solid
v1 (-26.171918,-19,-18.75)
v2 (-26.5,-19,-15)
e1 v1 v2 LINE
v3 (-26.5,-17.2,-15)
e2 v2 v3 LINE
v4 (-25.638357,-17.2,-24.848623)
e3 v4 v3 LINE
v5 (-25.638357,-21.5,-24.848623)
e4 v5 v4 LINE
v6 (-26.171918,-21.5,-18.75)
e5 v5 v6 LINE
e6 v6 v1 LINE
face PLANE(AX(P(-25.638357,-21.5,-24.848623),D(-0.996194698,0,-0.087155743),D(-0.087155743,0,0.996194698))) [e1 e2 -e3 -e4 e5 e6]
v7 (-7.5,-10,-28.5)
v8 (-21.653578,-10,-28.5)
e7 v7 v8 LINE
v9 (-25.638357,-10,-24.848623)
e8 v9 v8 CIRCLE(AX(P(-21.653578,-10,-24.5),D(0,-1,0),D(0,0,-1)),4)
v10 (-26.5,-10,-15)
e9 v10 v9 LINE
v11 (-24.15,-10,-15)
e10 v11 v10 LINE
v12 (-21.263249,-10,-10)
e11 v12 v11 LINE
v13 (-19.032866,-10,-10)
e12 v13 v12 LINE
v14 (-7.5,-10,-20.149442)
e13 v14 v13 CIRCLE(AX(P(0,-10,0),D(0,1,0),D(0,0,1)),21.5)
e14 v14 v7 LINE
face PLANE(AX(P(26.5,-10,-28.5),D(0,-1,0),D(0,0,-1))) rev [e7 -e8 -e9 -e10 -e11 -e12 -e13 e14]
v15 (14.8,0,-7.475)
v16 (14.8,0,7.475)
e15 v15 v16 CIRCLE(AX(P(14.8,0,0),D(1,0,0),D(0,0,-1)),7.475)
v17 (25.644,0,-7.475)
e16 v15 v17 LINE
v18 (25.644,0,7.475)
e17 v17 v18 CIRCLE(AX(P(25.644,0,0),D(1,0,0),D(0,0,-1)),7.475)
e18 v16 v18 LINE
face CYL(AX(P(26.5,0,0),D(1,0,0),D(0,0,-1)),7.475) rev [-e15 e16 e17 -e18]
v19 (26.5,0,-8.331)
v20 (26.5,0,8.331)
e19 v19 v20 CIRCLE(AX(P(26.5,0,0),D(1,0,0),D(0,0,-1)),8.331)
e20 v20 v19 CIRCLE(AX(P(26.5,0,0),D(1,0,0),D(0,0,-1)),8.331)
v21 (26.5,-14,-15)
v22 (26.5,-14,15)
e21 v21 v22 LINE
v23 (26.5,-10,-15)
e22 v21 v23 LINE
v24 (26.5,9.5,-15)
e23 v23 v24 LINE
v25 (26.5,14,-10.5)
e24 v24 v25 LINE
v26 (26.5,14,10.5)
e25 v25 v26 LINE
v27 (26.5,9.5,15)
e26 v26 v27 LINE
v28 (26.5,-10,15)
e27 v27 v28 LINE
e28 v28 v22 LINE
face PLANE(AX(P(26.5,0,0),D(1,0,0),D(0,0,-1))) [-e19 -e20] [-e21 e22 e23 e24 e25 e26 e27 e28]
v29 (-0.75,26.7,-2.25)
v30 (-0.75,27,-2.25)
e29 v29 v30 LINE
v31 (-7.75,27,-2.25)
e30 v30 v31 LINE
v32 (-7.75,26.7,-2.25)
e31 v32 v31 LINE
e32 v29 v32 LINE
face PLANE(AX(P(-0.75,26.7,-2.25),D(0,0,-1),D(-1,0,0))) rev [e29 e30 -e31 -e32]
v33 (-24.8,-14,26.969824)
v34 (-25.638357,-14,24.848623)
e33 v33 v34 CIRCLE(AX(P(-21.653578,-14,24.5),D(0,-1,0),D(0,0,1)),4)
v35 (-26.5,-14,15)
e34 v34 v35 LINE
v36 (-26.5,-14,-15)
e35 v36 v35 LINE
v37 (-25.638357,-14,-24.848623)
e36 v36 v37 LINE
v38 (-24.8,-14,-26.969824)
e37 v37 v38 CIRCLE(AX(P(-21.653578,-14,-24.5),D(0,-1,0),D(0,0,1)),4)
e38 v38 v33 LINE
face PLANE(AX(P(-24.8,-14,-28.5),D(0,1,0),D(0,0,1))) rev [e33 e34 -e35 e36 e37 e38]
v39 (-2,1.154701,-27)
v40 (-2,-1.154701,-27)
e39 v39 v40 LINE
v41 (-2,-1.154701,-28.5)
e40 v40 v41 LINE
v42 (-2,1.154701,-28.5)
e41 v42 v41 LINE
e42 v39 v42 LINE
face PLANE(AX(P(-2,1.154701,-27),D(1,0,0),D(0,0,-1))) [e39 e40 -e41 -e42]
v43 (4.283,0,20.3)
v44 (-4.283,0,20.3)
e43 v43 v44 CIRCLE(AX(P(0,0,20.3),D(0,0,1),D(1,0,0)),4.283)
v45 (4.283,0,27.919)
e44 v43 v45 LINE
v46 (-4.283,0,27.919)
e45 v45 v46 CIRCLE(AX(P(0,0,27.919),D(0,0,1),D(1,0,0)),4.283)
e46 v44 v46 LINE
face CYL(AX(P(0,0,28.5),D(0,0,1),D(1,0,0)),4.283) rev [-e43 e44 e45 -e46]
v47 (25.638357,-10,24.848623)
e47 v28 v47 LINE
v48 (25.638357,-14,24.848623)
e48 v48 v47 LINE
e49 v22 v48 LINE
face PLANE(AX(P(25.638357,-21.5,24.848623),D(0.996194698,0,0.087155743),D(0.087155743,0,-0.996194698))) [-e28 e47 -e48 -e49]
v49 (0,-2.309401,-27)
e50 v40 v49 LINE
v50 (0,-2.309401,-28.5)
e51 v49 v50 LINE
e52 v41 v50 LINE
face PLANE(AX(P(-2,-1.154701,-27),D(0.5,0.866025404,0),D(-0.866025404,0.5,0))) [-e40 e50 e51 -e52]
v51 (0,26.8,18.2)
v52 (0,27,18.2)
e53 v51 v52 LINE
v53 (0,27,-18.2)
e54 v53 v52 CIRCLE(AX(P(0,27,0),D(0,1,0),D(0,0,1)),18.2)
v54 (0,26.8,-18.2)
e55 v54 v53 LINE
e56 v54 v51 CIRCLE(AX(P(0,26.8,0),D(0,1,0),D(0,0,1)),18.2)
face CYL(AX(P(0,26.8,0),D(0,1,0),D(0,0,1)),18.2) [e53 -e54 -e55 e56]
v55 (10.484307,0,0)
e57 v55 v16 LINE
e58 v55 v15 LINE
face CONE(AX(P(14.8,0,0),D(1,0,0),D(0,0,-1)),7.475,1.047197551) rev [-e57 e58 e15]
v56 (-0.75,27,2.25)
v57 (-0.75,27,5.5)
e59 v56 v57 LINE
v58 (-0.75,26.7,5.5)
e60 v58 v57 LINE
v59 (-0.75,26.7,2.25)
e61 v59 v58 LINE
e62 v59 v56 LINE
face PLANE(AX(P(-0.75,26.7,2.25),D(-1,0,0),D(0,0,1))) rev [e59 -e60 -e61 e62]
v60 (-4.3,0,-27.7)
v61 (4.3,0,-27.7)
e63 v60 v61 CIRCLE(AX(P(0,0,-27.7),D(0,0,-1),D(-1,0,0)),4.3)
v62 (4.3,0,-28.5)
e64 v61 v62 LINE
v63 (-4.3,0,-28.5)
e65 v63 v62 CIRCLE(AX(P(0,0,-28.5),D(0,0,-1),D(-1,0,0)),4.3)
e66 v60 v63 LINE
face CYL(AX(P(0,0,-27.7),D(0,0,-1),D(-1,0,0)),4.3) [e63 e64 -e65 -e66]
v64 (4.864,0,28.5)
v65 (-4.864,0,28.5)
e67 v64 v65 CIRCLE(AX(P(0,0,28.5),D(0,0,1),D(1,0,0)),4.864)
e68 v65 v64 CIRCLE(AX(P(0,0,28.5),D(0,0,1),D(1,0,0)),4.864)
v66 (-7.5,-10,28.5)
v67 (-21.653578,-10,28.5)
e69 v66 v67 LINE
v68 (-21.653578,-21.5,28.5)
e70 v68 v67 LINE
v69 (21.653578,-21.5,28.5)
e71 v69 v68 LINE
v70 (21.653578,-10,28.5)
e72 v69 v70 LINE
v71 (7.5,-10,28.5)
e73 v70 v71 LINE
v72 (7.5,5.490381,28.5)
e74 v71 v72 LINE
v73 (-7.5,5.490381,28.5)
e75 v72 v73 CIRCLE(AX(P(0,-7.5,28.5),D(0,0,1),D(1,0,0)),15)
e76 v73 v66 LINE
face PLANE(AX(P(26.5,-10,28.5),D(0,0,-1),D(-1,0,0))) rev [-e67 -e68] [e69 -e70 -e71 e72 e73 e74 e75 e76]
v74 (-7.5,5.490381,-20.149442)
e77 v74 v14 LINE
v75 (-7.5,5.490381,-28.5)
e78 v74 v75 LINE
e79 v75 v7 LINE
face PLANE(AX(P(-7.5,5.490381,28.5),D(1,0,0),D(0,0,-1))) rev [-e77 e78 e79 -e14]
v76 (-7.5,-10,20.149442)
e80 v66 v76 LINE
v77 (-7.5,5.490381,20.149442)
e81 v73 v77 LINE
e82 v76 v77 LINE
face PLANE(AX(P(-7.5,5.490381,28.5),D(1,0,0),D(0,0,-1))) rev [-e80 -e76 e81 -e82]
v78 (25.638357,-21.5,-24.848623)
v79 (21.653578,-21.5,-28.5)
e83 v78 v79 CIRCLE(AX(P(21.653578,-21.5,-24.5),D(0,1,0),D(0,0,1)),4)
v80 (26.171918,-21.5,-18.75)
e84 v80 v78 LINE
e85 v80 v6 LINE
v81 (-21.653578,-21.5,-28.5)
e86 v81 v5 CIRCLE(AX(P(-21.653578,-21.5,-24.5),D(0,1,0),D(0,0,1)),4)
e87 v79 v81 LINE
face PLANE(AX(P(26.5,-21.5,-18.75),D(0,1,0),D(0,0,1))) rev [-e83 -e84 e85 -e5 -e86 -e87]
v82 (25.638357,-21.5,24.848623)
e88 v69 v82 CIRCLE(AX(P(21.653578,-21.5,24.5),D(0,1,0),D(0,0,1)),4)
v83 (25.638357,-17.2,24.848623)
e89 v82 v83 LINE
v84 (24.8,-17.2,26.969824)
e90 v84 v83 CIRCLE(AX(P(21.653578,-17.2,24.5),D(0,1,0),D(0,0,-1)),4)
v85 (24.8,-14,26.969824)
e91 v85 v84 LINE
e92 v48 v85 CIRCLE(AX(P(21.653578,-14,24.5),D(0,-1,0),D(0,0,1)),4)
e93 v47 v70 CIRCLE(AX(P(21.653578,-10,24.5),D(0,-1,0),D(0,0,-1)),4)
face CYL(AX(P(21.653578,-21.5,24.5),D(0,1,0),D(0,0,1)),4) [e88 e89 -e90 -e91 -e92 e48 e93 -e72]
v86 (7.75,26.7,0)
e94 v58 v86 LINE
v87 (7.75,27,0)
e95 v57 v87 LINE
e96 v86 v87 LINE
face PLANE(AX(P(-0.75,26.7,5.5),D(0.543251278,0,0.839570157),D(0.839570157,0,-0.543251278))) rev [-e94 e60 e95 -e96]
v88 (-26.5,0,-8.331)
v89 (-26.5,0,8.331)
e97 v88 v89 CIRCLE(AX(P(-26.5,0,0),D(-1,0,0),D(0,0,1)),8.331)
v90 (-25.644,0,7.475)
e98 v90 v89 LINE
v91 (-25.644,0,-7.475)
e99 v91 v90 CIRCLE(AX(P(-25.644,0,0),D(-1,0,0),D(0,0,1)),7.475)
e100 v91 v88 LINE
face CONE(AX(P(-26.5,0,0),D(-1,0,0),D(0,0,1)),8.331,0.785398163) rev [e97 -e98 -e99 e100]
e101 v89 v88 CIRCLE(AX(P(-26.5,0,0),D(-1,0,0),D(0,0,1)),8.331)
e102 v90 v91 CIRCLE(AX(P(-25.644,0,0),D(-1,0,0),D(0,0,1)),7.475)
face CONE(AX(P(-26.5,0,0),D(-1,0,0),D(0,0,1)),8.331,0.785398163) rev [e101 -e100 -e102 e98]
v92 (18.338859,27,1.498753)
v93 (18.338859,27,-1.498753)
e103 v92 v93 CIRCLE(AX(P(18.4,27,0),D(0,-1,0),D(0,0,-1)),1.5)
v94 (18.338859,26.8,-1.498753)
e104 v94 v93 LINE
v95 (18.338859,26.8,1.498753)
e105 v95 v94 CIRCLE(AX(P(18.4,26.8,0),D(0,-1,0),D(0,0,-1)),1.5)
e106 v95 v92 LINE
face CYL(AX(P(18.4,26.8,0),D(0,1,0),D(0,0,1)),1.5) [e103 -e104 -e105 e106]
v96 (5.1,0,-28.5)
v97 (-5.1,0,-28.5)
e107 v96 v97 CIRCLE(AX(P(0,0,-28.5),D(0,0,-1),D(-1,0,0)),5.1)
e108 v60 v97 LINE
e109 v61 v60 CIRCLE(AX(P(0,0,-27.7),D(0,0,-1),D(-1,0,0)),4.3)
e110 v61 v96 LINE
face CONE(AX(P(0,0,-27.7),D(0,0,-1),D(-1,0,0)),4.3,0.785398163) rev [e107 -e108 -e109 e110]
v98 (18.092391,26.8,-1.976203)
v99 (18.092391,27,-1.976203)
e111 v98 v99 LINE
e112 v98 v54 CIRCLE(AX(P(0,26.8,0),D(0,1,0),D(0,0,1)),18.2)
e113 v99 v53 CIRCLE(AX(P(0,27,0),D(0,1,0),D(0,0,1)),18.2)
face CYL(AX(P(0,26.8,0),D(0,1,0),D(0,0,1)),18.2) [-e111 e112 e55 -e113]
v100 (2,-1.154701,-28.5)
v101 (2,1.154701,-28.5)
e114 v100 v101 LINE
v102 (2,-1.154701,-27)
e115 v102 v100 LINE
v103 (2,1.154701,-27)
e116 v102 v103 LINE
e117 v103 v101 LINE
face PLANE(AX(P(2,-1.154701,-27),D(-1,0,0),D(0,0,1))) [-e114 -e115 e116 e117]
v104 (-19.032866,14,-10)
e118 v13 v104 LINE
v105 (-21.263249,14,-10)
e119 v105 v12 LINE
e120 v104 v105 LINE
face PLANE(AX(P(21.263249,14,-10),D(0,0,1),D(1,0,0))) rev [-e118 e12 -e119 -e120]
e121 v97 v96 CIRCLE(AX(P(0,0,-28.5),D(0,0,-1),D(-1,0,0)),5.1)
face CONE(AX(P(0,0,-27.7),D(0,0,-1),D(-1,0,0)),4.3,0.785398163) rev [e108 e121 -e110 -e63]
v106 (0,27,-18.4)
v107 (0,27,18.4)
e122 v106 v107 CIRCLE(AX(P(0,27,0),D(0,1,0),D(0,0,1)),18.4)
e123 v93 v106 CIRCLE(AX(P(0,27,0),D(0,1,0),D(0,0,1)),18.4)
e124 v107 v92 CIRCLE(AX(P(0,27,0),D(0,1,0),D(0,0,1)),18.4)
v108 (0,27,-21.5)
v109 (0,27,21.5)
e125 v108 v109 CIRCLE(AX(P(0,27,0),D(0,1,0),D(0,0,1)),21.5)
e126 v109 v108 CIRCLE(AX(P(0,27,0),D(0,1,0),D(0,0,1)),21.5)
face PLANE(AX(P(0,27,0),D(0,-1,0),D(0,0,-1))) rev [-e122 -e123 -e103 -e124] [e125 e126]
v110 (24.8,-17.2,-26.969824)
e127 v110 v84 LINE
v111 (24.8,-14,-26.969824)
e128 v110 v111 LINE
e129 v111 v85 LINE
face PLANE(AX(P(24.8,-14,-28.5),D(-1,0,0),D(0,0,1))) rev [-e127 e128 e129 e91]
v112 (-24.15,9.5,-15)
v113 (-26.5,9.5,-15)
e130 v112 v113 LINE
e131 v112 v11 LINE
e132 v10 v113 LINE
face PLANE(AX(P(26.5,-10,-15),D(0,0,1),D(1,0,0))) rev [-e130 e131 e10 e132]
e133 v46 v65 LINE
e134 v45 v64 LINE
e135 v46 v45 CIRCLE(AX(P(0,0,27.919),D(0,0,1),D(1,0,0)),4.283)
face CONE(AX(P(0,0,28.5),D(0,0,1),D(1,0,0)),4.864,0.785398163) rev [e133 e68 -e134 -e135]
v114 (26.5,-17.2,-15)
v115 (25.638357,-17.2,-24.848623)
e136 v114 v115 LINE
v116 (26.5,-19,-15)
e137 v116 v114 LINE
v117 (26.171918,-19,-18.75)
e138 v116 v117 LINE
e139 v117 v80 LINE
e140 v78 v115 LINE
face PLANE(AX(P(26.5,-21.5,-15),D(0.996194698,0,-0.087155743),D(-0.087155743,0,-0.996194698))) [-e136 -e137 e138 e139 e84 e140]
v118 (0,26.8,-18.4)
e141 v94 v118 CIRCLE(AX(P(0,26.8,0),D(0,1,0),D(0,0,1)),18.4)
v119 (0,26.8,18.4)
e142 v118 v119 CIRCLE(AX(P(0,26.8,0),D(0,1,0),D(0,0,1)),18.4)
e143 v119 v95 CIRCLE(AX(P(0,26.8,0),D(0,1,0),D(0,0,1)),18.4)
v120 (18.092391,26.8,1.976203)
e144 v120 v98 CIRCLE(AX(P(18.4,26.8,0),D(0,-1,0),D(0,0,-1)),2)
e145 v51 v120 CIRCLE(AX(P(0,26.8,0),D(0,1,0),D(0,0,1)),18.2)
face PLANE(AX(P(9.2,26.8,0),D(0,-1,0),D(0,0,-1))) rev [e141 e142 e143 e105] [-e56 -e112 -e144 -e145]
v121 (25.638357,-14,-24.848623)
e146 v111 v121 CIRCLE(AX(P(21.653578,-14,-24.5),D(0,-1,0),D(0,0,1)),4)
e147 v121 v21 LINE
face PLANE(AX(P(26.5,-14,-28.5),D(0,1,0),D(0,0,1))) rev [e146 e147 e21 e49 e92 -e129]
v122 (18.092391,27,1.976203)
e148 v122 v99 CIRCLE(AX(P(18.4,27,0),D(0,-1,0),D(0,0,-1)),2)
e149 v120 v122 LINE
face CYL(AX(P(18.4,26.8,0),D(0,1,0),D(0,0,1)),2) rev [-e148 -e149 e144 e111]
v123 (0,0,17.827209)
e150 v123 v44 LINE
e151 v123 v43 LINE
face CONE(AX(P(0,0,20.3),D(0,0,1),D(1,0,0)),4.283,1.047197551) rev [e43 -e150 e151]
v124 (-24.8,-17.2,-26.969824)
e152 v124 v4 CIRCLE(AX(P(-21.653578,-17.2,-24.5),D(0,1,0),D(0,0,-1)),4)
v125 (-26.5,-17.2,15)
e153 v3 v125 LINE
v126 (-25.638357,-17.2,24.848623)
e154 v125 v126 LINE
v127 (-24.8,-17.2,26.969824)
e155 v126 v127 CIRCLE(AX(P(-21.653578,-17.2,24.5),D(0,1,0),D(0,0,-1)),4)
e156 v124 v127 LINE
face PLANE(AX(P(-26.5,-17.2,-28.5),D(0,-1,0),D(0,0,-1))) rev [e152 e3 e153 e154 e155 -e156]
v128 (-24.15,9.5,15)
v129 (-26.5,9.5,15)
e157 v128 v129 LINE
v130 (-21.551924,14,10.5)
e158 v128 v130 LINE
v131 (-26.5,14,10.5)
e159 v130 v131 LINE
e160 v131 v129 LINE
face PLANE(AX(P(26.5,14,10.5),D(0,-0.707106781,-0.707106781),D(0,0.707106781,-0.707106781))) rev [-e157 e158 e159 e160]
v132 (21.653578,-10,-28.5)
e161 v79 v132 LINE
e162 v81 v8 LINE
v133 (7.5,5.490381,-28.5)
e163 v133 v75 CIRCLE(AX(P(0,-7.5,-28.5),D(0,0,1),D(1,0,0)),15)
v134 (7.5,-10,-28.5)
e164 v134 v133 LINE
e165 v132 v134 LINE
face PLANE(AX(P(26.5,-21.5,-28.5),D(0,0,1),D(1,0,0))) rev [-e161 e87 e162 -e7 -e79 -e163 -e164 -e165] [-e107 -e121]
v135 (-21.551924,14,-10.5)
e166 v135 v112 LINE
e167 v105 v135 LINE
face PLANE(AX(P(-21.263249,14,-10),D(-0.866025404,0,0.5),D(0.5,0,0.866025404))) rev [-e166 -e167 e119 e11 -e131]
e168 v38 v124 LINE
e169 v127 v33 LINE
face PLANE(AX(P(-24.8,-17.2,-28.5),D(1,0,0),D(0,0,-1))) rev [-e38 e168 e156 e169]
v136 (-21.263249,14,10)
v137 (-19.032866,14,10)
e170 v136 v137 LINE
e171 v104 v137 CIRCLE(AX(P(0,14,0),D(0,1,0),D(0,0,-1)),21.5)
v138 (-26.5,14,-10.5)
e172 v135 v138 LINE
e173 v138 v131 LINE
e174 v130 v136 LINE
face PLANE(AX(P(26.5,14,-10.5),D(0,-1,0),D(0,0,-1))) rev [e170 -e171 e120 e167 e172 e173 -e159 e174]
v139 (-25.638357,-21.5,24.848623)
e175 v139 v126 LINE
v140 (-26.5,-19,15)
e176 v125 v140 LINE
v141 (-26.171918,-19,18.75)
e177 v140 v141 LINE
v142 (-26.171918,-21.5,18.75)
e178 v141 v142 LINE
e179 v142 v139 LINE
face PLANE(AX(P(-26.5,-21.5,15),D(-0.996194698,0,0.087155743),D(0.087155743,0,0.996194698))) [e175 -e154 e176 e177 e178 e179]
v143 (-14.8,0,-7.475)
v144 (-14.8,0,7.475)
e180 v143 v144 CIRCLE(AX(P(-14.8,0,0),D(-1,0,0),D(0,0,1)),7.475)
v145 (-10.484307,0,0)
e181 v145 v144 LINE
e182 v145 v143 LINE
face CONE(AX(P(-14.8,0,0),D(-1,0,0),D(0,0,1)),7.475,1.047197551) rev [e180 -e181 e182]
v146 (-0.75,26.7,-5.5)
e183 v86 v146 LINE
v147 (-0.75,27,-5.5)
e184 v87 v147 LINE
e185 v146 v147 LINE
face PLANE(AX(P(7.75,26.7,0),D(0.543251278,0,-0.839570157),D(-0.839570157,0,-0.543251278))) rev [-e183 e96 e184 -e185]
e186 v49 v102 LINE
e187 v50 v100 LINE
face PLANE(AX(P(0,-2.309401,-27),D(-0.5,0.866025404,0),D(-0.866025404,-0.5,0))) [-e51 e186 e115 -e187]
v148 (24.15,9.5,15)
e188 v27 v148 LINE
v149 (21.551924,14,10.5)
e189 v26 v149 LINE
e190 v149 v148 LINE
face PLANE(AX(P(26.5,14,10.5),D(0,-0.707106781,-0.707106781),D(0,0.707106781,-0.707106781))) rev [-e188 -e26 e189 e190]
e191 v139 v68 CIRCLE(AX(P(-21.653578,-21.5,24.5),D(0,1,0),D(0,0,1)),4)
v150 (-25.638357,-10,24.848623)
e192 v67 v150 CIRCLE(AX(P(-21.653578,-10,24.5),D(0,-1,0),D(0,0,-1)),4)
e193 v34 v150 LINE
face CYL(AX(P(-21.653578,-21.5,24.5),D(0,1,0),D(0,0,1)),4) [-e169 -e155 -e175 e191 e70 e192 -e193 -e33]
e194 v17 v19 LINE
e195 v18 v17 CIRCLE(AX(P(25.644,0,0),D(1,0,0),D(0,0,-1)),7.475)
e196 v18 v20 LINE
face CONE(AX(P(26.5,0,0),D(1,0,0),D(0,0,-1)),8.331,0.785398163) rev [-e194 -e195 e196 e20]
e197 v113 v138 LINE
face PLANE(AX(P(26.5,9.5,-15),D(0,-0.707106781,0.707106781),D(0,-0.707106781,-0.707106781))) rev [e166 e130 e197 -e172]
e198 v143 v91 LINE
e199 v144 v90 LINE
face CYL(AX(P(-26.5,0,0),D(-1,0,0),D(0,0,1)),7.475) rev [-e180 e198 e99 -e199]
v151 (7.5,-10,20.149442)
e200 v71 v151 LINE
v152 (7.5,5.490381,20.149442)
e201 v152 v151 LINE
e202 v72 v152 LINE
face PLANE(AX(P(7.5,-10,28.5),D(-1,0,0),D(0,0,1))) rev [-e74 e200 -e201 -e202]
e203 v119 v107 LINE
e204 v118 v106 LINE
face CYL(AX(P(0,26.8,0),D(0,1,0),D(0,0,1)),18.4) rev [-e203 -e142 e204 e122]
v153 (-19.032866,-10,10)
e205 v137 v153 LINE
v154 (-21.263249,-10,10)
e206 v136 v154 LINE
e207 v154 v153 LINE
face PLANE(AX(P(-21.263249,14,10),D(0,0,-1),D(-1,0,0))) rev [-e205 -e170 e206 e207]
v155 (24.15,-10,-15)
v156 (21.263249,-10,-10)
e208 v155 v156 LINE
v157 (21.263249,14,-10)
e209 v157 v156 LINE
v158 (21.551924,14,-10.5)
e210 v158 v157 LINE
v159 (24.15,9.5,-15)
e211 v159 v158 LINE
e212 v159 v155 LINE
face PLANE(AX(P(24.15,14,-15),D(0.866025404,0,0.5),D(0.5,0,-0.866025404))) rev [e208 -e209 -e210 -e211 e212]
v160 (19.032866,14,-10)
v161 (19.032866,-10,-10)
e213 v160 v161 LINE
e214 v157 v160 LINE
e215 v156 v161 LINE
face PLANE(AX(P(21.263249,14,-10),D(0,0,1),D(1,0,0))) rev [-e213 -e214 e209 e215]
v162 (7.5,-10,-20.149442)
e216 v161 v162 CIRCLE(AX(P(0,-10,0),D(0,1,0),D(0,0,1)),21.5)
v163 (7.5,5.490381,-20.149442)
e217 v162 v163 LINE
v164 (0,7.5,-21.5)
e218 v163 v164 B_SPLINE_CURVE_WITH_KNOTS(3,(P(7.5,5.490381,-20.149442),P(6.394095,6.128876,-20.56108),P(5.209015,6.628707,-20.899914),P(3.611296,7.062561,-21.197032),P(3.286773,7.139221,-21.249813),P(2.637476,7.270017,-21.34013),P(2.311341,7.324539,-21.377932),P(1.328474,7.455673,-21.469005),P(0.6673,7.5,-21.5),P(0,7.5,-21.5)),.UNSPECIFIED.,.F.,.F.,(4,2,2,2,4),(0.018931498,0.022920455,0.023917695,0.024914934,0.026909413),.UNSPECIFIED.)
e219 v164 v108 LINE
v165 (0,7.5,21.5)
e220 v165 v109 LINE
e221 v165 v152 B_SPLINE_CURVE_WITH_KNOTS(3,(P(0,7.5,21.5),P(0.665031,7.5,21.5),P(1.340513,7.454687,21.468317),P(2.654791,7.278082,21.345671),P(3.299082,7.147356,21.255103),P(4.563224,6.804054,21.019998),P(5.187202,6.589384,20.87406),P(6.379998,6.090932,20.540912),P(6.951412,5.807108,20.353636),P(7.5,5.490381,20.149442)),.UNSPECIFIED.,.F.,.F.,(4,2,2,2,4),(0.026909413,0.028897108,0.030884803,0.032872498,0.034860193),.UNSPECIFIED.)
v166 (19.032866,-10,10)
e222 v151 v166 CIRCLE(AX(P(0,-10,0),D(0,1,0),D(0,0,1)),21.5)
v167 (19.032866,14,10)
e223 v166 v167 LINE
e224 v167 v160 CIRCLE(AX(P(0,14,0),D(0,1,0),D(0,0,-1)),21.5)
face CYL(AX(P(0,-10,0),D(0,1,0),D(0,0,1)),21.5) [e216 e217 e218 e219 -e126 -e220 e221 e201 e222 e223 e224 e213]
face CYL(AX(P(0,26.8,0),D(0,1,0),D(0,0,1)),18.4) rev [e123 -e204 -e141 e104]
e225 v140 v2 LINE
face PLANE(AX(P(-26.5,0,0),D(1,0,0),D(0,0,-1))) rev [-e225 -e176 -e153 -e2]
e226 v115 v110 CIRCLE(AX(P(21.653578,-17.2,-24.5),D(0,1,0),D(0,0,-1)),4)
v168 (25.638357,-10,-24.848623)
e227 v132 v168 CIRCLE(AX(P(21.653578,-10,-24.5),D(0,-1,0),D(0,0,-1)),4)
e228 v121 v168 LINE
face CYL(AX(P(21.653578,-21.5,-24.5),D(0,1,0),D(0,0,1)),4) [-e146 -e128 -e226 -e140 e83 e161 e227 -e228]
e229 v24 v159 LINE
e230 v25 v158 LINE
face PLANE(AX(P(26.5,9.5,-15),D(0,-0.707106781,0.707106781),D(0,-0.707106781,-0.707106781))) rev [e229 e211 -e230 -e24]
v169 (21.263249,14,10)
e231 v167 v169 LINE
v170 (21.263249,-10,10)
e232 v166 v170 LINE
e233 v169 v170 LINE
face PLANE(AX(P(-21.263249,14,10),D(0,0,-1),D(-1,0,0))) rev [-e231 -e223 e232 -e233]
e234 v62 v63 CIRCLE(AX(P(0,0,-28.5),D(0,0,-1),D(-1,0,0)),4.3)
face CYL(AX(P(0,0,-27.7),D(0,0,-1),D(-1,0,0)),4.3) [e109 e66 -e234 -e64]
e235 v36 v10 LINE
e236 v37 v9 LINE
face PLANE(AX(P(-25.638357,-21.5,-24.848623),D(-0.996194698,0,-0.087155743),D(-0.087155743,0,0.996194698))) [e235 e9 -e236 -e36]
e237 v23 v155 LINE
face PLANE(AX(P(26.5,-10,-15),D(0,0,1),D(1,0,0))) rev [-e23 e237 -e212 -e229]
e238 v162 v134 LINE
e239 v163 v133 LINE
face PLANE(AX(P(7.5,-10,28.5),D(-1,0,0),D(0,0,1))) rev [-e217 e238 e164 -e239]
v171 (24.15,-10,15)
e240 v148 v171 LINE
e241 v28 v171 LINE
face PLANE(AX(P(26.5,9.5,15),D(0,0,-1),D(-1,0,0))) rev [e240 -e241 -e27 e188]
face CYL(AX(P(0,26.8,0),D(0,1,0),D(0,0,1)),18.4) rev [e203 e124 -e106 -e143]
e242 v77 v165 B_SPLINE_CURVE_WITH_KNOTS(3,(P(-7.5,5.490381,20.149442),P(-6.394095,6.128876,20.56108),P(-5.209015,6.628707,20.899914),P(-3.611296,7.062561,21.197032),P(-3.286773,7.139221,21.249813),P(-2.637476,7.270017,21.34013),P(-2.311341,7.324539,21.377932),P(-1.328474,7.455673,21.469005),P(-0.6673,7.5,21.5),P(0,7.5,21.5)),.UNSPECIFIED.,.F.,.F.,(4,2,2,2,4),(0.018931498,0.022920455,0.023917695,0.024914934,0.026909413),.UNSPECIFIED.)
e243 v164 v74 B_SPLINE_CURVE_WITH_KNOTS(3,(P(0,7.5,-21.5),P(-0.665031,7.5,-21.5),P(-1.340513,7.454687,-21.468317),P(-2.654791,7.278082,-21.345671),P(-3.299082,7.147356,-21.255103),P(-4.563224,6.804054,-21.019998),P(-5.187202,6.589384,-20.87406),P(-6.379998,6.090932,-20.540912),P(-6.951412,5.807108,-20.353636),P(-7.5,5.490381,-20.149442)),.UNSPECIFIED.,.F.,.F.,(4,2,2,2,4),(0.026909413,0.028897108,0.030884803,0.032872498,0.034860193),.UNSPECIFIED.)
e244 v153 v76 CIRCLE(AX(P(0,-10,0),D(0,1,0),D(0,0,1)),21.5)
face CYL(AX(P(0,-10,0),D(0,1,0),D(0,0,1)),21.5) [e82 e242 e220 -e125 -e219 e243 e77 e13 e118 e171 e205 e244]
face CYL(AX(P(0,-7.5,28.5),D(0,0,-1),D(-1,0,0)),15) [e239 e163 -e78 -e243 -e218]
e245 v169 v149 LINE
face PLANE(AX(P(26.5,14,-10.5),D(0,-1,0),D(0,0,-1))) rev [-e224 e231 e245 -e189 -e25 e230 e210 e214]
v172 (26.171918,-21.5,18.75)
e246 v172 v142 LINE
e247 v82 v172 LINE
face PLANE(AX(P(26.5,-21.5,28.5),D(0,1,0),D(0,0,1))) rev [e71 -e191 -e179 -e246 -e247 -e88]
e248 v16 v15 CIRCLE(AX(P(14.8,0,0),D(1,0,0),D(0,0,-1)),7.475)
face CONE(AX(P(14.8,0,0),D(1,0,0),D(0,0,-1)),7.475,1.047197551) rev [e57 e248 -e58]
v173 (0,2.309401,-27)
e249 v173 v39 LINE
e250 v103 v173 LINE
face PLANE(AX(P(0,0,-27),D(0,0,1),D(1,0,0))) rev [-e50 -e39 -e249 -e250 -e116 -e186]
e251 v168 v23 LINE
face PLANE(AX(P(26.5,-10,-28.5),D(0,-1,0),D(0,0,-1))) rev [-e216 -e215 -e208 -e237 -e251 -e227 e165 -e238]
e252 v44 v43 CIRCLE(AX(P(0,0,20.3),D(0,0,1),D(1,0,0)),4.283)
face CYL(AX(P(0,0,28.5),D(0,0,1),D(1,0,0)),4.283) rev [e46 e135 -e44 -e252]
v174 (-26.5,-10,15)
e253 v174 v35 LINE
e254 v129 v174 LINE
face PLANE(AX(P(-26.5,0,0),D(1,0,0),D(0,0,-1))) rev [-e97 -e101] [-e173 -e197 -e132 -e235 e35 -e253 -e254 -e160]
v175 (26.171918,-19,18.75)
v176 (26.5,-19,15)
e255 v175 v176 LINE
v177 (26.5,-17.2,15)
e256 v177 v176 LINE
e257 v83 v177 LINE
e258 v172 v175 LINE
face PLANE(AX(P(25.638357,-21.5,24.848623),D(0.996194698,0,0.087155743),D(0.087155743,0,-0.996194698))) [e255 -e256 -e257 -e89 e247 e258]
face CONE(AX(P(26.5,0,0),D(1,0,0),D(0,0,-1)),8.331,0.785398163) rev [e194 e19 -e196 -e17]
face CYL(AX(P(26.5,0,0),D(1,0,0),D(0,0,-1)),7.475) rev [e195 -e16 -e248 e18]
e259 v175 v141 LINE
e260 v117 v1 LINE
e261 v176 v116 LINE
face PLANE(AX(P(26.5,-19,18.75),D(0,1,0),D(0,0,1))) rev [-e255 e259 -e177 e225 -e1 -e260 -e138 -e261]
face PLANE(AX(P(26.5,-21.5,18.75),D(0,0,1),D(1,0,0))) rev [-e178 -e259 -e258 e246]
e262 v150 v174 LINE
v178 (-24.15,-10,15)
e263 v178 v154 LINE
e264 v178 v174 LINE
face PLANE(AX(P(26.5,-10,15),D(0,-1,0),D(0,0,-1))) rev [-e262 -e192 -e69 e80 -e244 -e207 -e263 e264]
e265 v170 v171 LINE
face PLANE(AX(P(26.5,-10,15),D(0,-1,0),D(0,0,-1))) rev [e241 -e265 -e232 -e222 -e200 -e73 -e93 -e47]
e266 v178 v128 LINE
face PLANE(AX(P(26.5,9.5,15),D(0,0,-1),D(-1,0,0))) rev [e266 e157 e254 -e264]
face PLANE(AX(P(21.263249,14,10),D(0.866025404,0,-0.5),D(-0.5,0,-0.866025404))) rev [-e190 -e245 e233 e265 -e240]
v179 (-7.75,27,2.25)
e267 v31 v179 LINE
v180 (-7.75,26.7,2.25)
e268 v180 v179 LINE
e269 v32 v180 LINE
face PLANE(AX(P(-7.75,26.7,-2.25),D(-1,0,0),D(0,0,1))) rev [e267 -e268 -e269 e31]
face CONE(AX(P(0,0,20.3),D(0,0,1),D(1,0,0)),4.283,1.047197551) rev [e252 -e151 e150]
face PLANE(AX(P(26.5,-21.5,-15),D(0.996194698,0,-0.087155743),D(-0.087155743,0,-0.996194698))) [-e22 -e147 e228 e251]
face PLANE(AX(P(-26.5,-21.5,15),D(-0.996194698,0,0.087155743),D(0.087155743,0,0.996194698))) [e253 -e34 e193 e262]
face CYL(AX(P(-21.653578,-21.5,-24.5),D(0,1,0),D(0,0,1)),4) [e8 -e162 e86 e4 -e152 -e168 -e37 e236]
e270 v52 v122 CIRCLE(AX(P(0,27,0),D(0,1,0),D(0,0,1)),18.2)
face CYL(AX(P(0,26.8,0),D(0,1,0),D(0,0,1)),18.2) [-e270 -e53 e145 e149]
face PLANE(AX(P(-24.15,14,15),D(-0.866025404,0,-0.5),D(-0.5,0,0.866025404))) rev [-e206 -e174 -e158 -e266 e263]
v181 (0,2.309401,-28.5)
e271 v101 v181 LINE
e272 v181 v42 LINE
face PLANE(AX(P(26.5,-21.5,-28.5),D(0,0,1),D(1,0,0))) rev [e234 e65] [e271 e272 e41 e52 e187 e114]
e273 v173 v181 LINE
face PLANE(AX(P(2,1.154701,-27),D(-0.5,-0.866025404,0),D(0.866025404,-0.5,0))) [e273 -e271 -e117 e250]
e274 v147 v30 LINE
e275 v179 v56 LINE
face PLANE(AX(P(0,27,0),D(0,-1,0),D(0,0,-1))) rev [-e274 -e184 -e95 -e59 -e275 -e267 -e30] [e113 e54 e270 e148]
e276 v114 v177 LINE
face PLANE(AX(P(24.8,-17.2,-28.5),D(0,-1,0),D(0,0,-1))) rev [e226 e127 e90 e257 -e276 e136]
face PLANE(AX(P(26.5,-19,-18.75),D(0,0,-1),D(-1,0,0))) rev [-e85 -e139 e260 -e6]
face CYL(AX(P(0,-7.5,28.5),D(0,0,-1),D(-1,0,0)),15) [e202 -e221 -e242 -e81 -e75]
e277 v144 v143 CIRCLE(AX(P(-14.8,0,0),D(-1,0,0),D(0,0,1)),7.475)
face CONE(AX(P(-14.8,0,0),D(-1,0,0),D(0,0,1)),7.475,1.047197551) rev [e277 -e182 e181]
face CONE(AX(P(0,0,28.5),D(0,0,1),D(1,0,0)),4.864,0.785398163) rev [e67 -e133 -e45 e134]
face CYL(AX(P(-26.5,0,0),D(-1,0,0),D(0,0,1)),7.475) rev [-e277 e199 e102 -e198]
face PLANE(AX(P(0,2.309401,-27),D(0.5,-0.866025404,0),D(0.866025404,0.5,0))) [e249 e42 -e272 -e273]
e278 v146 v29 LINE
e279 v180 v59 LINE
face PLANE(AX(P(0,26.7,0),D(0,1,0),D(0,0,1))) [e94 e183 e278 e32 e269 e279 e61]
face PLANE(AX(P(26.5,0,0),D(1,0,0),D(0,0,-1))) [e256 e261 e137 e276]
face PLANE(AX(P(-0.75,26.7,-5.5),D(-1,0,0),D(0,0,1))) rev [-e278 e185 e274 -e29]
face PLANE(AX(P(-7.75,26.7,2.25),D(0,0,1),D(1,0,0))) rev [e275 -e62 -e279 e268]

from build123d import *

# Parameters (mm, degrees)
EXTRUDE_1_DEPTH           = 26.5
EXTRUDE_1_DEPTH_BACK      = 26.5
SKETCH_2_W                = 57
SKETCH_2_H                = 61
CUT_EXTRUDE_1_DEPTH       = 21.5
SKETCH_3_W                = 57
SKETCH_3_H                = 34
CUT_EXTRUDE_2_DEPTH       = 24
EXTRUDE_2_DEPTH           = 28.5
EXTRUDE_2_DEPTH_BACK      = 28.5
SKETCH_5_W                = 21.5
SKETCH_5_H                = 37
CUT_EXTRUDE_3_DEPTH       = 28.5
CUT_EXTRUDE_3_DEPTH_BACK  = 28.5
SKETCH_6_W                = 1.7
SKETCH_6_H                = 3.2
CUT_EXTRUDE_4_DEPTH       = 28.5
CUT_EXTRUDE_4_DEPTH_BACK  = 28.5
SKETCH_7_W                = 1.7
SKETCH_7_H                = 3.2
HOLE_WIZARD_1_D           = 8.566
HOLE_WIZARD_1_DEPTH       = 8.2
HOLE_WIZARD_1_CSINK_D     = 9.728
HOLE_WIZARD_1_CSINK_ANGLE = 90
HOLE_WIZARD_1_TIP         = 2.472791203
CUT_EXTRUDE_5_DEPTH       = 1.5
HOLE_WIZARD_2_D           = 14.95
HOLE_WIZARD_2_DEPTH       = 11.7
HOLE_WIZARD_2_CSINK_D     = 16.662
HOLE_WIZARD_2_CSINK_ANGLE = 90
HOLE_WIZARD_2_TIP         = 4.315693262
HOLE_WIZARD_3_D           = 14.95
HOLE_WIZARD_3_DEPTH       = 11.7
HOLE_WIZARD_3_CSINK_D     = 16.662
HOLE_WIZARD_3_CSINK_ANGLE = 90
HOLE_WIZARD_3_TIP         = 4.315693262
CUT_EXTRUDE_6_DEPTH       = 0.3
CUT_EXTRUDE_7_DEPTH       = 0.2


with BuildPart() as part:
    # 草图1 → 凸台-拉伸1 (new, two sides: drawn at the far end of the back side and taken through both)
    with BuildSketch(Plane(origin=(0, 0, 0), x_dir=(0, 0, -1), z_dir=(1, 0, 0)).offset(-EXTRUDE_1_DEPTH_BACK)):
        Polygon((-28.5, -21.5), (-18.75, -21.5), (-18.75, -19), (18.75, -19), (18.75, -21.5), (28.5, -21.5), (28.5, -10), (15, -10), (15, 9.5), (10.5, 14), (-10.5, 14), (-15, 9.5), (-15, -10), (-28.5, -10), align=None)
    extrude(amount=EXTRUDE_1_DEPTH + EXTRUDE_1_DEPTH_BACK)

    # 草图2 → 切除-拉伸1 (cut)
    with BuildSketch(Plane(origin=(0, 0, 0), x_dir=(1, 0, 0), z_dir=(0, 1, 0))):
        Rectangle(SKETCH_2_W, SKETCH_2_H)
        with BuildLine():
            Line((-26.5, -15), (-25.638357139, -24.848622971))
            ThreePointArc((-25.638357139, -24.848622971), (-24.355939177, -27.449109347), (-21.653578346, -28.5))
            Line((-21.653578346, -28.5), (21.653578346, -28.5))
            ThreePointArc((21.653578346, -28.5), (24.355939177, -27.449109347), (25.638357139, -24.848622971))
            Line((25.638357139, -24.848622971), (26.5, -15))
            Line((26.5, -15), (26.5, 15))
            Line((26.5, 15), (25.638357139, 24.848622971))
            ThreePointArc((25.638357139, 24.848622971), (24.355939177, 27.449109347), (21.653578346, 28.5))
            Line((21.653578346, 28.5), (-21.653578346, 28.5))
            ThreePointArc((-21.653578346, 28.5), (-24.355939177, 27.449109347), (-25.638357139, 24.848622971))
            Line((-25.638357139, 24.848622971), (-26.5, 15))
            Line((-26.5, 15), (-26.5, -15))
        make_face(mode=Mode.SUBTRACT)
    extrude(amount=-CUT_EXTRUDE_1_DEPTH, mode=Mode.SUBTRACT)

    # 草图3 → 切除-拉伸2 (cut)
    with BuildSketch(Plane(origin=(0, -10, 0), x_dir=(1, 0, 0), z_dir=(0, 1, 0))):
        Rectangle(SKETCH_3_W, SKETCH_3_H)
        Polygon((-26.5, -15), (-24.15, -15), (-21.263248654, -10), (21.263248654, -10), (24.15, -15), (26.5, -15), (26.5, 15), (24.15, 15), (21.263248654, 10), (-21.263248654, 10), (-24.15, 15), (-26.5, 15), align=None, mode=Mode.SUBTRACT)
    extrude(amount=CUT_EXTRUDE_2_DEPTH, mode=Mode.SUBTRACT)

    # 草图4 → 凸台-拉伸2 (add, two sides: drawn at the far end of the back side and taken through both)
    with BuildSketch(Plane.XY.offset(-EXTRUDE_2_DEPTH_BACK)):
        with BuildLine():
            Line((-7.5, -10), (7.5, -10))
            Line((7.5, -10), (7.5, 5.490381057))
            ThreePointArc((7.5, 5.490381057), (0, 7.5), (-7.5, 5.490381057))
            Line((-7.5, 5.490381057), (-7.5, -10))
        make_face()
    extrude(amount=EXTRUDE_2_DEPTH + EXTRUDE_2_DEPTH_BACK)

    # 草图5 → 旋转1 (revolve)
    with BuildSketch(Plane.XY, mode=Mode.PRIVATE) as revolve_1_sk:
        with Locations((10.75, 8.5)):
            Rectangle(SKETCH_5_W, SKETCH_5_H)
    revolve(revolve_1_sk.sketch.rotate(Axis((0, -10, 0), (0, 1, 0)), 270), axis=Axis((0, -10, 0), (0, 1, 0)))

    # 草图6 → 切除-拉伸3 (cut, two sides: drawn at the far end of the back side and taken through both)
    with BuildSketch(Plane.XY.offset(-CUT_EXTRUDE_3_DEPTH_BACK)):
        with Locations((25.65, -15.6)):
            Rectangle(SKETCH_6_W, SKETCH_6_H)
    extrude(amount=CUT_EXTRUDE_3_DEPTH + CUT_EXTRUDE_3_DEPTH_BACK, mode=Mode.SUBTRACT)

    # 草图7 → 切除-拉伸4 (cut, two sides: drawn at the far end of the back side and taken through both)
    with BuildSketch(Plane.XY.offset(-CUT_EXTRUDE_4_DEPTH_BACK)):
        with Locations((-25.65, -15.6)):
            Rectangle(SKETCH_7_W, SKETCH_7_H)
    extrude(amount=CUT_EXTRUDE_4_DEPTH + CUT_EXTRUDE_4_DEPTH_BACK, mode=Mode.SUBTRACT)

    # 草图8 → 切除-旋转1 (revolve, cut)
    with BuildSketch(Plane(origin=(0, 0, 0), x_dir=(1, 0, 0), z_dir=(0, 1, 0)), mode=Mode.PRIVATE) as cut_revolve_1_sk:
        Polygon((4.3, 28.5), (4.3, 27.7), (5.1, 28.5), align=None)
    revolve(cut_revolve_1_sk.sketch.rotate(Axis((0, 0, -27.7), (0, 0, -1)), 180), axis=Axis((0, 0, -27.7), (0, 0, -1)), mode=Mode.SUBTRACT)

    # 孔1
    with Locations(Plane.XY.offset(28.5)):
        with Locations((0, 0)):
            CounterSinkHole(HOLE_WIZARD_1_D / 2, HOLE_WIZARD_1_CSINK_D / 2, depth=HOLE_WIZARD_1_DEPTH, counter_sink_angle=HOLE_WIZARD_1_CSINK_ANGLE)
            with Locations((0, 0, -(HOLE_WIZARD_1_DEPTH + HOLE_WIZARD_1_TIP / 2))):  # 120° drill point
                Cone(0, HOLE_WIZARD_1_D / 2, HOLE_WIZARD_1_TIP, mode=Mode.SUBTRACT)

    # 草图11 → 切除-拉伸5 (cut)
    with BuildSketch(Plane.XY.offset(-28.5)):
        Polygon((-2, 1.154700538), (-2, -1.154700538), (0, -2.309401077), (2, -1.154700538), (2, 1.154700538), (0, 2.309401077), align=None)
    extrude(amount=CUT_EXTRUDE_5_DEPTH, mode=Mode.SUBTRACT)

    # 孔2
    with Locations(Plane(origin=(26.5, 0, 0), x_dir=(0, 0, -1), z_dir=(1, 0, 0))):
        with Locations((0, 0)):
            CounterSinkHole(HOLE_WIZARD_2_D / 2, HOLE_WIZARD_2_CSINK_D / 2, depth=HOLE_WIZARD_2_DEPTH, counter_sink_angle=HOLE_WIZARD_2_CSINK_ANGLE)
            with Locations((0, 0, -(HOLE_WIZARD_2_DEPTH + HOLE_WIZARD_2_TIP / 2))):  # 120° drill point
                Cone(0, HOLE_WIZARD_2_D / 2, HOLE_WIZARD_2_TIP, mode=Mode.SUBTRACT)

    # 孔3
    with Locations(Plane.ZY.offset(26.5)):
        with Locations((0, 0)):
            CounterSinkHole(HOLE_WIZARD_3_D / 2, HOLE_WIZARD_3_CSINK_D / 2, depth=HOLE_WIZARD_3_DEPTH, counter_sink_angle=HOLE_WIZARD_3_CSINK_ANGLE)
            with Locations((0, 0, -(HOLE_WIZARD_3_DEPTH + HOLE_WIZARD_3_TIP / 2))):  # 120° drill point
                Cone(0, HOLE_WIZARD_3_D / 2, HOLE_WIZARD_3_TIP, mode=Mode.SUBTRACT)

    # 草图16 → 切除-拉伸6 (cut)
    with BuildSketch(Plane(origin=(0, 27, 0), x_dir=(1, 0, 0), z_dir=(0, 1, 0))):
        Polygon((-7.75, -2.25), (-0.75, -2.25), (-0.75, -5.5), (7.75, 0), (-0.75, 5.5), (-0.75, 2.25), (-7.75, 2.25), align=None)
    extrude(amount=-CUT_EXTRUDE_6_DEPTH, mode=Mode.SUBTRACT)

    # 草图17 → 切除-拉伸7 (cut)
    with BuildSketch(Plane(origin=(0, 27, 0), x_dir=(1, 0, 0), z_dir=(0, 1, 0))):
        with BuildLine():
            ThreePointArc((18.338858696, 1.498753396), (-18.4, 0), (18.338858696, -1.498753396))
            ThreePointArc((18.338858696, -1.498753396), (16.9, 0), (18.338858696, 1.498753396))
        make_face()
        with BuildLine():
            ThreePointArc((18.092391304, 1.976202644), (-18.2, 0), (18.092391304, -1.976202644))
            ThreePointArc((18.092391304, -1.976202644), (16.4, 0), (18.092391304, 1.976202644))
        make_face(mode=Mode.SUBTRACT)
    extrude(amount=-CUT_EXTRUDE_7_DEPTH, mode=Mode.SUBTRACT)


solid = part.part
